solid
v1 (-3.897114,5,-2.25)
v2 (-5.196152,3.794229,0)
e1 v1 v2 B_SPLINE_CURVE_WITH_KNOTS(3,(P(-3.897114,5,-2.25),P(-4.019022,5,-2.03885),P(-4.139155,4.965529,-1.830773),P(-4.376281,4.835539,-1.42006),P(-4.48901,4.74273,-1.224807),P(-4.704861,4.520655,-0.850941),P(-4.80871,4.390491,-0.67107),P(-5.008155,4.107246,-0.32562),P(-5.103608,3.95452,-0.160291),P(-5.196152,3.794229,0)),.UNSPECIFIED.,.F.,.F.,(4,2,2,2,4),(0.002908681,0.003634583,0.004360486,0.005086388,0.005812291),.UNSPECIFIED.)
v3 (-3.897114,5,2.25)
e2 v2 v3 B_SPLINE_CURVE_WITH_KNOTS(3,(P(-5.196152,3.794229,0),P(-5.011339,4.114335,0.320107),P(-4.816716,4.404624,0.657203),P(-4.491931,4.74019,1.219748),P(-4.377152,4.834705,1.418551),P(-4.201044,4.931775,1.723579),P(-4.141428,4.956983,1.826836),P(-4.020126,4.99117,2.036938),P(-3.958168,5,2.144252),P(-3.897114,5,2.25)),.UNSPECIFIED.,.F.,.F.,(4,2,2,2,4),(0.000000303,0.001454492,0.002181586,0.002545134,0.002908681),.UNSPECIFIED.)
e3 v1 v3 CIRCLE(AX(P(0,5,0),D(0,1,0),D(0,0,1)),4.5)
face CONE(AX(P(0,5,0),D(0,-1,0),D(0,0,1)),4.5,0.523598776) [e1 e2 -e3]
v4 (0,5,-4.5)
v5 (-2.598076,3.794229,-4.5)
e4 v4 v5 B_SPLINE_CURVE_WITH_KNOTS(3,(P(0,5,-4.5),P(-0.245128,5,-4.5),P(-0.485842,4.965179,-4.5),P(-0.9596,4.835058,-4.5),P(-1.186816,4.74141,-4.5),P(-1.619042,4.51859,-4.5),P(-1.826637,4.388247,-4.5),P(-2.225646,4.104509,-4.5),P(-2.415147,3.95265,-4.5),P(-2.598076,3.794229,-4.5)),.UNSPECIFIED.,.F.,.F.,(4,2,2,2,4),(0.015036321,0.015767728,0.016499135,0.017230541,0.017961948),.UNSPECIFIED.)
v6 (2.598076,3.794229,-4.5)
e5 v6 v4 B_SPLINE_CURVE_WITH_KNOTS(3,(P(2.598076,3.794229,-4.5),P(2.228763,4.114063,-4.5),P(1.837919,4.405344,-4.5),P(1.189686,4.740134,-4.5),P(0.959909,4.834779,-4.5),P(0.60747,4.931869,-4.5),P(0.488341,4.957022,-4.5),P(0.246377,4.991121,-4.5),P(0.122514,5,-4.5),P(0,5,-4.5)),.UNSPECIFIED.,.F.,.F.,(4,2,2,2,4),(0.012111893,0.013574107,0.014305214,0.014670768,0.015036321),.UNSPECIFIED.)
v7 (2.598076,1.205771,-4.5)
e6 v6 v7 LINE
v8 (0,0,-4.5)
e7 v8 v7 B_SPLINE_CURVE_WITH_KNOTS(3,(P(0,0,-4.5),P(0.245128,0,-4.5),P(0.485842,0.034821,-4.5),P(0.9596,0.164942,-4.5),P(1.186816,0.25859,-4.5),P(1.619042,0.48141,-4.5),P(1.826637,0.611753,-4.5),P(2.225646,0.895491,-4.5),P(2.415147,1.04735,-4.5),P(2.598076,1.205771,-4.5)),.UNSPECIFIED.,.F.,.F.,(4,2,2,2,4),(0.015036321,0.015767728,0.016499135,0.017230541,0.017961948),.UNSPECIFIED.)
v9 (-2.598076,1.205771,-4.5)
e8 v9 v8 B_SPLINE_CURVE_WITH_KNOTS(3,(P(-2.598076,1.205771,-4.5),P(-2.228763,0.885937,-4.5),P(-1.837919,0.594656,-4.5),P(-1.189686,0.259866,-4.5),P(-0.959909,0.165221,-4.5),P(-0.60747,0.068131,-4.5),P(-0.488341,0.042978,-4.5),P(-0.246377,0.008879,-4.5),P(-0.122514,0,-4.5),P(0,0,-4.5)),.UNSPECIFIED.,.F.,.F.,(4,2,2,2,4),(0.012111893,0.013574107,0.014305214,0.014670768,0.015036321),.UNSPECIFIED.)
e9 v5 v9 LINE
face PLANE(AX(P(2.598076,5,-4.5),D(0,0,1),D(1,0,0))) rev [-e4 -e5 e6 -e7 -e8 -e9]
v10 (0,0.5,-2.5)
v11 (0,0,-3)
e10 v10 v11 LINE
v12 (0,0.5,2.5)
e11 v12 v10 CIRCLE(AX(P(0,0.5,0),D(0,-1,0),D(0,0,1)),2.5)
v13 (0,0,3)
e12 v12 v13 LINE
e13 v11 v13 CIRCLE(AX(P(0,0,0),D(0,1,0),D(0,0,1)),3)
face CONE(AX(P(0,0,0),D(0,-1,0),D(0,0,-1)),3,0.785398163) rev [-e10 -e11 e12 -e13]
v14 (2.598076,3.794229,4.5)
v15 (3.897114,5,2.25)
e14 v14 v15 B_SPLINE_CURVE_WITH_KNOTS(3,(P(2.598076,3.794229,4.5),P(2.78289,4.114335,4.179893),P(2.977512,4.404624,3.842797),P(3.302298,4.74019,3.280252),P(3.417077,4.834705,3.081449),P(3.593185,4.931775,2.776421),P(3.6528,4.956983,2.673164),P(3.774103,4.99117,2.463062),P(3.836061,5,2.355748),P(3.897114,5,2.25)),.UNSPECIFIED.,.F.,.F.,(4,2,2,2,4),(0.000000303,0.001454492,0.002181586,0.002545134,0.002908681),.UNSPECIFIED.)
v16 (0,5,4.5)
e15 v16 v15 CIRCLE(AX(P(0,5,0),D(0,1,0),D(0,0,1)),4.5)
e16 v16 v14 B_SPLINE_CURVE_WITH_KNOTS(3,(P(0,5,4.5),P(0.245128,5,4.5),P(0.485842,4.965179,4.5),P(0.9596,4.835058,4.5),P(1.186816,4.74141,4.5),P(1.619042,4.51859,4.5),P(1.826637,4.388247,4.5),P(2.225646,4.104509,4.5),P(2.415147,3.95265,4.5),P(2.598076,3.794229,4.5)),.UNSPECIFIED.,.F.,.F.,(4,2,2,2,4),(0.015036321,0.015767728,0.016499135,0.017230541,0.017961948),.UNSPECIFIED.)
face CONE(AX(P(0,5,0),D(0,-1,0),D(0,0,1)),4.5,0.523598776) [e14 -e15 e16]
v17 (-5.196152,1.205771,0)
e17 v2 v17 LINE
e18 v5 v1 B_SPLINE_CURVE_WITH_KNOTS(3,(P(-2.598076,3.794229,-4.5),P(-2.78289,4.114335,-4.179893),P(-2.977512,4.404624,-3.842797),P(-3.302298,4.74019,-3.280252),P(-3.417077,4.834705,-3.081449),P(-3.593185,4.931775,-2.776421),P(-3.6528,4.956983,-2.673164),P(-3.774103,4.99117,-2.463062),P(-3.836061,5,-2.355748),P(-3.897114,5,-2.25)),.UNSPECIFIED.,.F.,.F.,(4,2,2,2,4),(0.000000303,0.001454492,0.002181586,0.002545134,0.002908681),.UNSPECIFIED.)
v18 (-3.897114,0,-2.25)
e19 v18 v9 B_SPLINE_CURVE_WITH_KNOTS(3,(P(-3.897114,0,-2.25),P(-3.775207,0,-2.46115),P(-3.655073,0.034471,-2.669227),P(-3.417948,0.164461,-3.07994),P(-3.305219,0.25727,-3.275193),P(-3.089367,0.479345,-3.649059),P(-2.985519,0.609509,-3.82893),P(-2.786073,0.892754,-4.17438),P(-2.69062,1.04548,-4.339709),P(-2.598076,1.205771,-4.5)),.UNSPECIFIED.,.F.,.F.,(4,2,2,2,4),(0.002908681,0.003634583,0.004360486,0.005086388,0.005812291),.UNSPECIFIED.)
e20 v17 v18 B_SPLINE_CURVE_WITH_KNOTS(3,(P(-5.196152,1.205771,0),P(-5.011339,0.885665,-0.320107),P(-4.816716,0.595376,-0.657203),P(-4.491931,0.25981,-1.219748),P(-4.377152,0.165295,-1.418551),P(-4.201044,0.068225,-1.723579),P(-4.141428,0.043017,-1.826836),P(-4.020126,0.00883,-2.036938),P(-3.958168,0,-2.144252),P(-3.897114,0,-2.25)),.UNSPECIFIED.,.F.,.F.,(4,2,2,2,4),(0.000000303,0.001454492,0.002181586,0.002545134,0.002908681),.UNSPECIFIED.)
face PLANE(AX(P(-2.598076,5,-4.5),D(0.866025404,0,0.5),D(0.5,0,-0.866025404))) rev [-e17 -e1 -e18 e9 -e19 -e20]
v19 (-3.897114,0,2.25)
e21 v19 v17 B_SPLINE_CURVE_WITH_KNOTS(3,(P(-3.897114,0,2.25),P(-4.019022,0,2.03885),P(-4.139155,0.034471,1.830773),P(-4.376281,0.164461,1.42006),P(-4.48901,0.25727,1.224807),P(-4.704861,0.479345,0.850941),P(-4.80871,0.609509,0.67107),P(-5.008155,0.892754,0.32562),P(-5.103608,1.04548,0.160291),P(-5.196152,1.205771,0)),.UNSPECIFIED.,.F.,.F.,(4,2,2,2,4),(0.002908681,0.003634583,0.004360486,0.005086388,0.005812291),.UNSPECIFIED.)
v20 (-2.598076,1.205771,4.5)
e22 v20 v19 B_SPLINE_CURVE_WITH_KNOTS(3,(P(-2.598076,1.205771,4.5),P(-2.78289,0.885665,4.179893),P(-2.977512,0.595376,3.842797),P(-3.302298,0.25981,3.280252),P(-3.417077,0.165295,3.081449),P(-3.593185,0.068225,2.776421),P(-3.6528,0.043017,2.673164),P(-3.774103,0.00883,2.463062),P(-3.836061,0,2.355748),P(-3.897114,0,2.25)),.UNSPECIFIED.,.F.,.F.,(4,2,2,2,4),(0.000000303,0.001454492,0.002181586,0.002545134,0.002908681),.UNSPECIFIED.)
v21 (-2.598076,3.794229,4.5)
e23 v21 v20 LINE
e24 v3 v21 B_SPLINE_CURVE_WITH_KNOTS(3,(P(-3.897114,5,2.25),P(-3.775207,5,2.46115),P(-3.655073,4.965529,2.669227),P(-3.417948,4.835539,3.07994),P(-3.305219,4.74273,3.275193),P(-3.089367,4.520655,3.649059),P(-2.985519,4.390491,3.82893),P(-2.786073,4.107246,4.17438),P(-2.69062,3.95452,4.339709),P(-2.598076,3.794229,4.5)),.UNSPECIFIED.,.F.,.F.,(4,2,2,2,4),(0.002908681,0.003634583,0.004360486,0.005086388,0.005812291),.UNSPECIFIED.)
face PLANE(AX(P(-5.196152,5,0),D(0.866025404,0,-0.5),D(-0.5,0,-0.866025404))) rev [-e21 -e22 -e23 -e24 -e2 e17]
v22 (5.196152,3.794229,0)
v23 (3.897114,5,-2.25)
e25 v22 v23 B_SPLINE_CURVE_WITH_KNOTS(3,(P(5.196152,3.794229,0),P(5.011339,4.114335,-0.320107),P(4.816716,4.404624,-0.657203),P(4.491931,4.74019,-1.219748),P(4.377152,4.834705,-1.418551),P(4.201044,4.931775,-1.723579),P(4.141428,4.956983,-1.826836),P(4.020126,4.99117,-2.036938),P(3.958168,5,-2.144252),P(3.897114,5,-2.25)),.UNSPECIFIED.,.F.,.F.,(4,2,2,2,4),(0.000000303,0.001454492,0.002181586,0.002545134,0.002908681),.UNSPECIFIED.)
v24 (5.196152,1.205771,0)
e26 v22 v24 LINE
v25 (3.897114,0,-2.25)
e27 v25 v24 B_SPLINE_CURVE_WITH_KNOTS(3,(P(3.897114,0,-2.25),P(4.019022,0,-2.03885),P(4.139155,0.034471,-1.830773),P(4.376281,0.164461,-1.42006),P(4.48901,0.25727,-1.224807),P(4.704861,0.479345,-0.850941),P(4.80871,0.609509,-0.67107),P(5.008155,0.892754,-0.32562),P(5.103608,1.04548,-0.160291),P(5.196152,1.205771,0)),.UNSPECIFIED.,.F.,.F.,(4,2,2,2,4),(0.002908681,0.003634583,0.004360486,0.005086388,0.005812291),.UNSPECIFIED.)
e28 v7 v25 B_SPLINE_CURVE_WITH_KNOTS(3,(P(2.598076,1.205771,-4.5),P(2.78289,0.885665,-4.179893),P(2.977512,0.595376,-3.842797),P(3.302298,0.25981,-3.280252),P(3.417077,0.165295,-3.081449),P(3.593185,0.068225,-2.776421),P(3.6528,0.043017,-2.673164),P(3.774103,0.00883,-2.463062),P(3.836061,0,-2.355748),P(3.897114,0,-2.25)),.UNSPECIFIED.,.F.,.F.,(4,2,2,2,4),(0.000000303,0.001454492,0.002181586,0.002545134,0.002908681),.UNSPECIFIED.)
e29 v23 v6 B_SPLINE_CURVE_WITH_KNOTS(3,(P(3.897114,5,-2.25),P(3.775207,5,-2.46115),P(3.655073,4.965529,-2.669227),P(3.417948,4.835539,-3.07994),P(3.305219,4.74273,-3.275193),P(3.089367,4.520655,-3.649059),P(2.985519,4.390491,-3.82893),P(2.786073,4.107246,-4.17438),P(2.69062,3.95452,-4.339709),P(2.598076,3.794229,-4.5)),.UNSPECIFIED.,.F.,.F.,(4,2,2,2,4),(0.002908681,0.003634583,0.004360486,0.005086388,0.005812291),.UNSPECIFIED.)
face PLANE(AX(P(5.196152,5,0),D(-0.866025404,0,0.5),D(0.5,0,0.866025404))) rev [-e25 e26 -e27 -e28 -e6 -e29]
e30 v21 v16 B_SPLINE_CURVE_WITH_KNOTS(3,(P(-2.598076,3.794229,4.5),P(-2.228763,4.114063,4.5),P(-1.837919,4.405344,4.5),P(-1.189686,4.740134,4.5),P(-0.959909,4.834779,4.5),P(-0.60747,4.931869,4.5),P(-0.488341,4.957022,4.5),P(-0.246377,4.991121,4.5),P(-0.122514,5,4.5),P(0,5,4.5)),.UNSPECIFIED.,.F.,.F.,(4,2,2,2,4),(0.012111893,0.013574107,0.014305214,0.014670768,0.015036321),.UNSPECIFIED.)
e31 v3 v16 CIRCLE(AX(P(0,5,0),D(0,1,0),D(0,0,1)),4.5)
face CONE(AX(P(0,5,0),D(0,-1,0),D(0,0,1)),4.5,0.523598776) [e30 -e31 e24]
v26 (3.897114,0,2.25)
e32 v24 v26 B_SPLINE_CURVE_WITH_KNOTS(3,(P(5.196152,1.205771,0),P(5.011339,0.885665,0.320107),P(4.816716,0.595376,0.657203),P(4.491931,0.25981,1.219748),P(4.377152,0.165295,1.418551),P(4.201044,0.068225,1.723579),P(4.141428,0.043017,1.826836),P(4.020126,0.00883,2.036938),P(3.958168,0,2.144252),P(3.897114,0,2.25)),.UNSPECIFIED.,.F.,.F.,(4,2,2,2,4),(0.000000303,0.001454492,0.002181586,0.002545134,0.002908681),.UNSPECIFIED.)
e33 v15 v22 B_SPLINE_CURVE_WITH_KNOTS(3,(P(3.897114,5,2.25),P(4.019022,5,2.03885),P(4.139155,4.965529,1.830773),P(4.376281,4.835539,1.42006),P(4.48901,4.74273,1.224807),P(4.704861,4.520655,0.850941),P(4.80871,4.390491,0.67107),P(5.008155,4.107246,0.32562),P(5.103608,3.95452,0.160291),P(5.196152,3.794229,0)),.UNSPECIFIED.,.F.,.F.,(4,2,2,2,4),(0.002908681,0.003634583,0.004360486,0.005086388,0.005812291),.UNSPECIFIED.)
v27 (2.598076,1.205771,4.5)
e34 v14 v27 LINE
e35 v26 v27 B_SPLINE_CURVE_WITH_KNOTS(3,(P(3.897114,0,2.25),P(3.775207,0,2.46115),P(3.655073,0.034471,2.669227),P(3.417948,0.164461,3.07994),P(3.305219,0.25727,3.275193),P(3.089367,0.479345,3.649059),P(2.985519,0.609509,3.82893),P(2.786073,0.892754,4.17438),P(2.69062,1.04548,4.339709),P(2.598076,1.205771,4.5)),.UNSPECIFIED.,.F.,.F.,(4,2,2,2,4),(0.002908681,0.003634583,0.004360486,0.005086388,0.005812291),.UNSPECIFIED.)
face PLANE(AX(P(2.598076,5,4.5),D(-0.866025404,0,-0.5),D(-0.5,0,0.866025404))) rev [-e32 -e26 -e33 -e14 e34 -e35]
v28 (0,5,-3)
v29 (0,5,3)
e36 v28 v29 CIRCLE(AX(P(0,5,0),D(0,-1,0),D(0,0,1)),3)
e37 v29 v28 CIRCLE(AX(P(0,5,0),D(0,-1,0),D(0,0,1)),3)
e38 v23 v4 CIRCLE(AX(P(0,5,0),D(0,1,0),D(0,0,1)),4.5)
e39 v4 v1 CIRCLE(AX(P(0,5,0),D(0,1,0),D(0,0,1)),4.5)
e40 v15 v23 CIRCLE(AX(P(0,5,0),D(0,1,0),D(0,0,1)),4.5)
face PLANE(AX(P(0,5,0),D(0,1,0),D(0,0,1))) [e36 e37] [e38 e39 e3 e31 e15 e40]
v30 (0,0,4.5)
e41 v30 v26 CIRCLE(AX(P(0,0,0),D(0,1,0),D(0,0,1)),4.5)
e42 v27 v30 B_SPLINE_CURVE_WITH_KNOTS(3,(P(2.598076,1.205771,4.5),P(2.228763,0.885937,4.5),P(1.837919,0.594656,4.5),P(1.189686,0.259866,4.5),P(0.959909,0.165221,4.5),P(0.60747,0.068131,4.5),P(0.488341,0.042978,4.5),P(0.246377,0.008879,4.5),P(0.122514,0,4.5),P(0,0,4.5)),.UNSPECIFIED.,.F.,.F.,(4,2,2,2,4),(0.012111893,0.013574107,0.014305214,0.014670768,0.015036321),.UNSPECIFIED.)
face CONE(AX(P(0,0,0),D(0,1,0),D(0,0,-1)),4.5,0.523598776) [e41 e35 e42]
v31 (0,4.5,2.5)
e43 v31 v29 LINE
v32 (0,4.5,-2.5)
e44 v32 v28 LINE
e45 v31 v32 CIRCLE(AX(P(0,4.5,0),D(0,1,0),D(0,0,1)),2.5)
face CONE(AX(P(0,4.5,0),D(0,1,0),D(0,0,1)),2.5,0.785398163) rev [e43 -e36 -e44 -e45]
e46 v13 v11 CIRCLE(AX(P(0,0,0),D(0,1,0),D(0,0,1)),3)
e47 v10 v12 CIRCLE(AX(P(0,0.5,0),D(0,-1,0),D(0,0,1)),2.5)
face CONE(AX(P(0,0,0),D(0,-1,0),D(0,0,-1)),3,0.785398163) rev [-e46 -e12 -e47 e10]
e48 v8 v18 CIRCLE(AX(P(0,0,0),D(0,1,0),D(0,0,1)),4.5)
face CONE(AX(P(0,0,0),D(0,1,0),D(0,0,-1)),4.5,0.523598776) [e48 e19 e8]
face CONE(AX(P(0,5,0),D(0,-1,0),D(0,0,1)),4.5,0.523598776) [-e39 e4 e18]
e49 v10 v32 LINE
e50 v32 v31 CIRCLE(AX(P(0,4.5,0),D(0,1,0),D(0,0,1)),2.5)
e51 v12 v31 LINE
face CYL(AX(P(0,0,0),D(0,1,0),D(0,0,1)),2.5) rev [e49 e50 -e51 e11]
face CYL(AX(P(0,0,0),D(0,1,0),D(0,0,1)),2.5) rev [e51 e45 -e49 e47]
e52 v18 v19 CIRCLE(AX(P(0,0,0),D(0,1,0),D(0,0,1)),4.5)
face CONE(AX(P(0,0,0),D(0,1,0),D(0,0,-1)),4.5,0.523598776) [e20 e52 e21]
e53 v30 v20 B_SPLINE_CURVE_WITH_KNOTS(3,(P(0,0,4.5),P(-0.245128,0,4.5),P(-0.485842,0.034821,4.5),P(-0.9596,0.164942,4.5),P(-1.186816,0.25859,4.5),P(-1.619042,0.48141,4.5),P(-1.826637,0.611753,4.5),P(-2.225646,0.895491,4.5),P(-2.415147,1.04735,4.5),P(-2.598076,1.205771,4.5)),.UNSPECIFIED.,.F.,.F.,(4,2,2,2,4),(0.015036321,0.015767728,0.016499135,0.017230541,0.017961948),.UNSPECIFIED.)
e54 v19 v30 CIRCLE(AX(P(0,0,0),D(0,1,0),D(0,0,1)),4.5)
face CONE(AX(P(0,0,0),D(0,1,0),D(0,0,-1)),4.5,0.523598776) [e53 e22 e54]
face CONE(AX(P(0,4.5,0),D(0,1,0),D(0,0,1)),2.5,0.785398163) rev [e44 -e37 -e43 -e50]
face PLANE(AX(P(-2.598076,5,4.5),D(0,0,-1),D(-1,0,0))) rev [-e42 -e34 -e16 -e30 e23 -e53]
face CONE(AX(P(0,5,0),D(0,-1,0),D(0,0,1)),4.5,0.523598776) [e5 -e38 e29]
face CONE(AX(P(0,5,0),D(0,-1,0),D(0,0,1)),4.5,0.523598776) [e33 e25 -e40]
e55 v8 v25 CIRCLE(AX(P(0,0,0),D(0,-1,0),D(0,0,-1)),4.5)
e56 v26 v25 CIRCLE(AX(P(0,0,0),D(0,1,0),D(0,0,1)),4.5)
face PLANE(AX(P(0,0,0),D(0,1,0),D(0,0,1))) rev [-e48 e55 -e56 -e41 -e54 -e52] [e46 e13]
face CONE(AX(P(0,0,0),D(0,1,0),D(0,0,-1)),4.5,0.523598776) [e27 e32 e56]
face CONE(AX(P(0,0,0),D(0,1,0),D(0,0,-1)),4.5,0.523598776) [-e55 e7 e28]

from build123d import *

# Parameters (mm, degrees)
BOSS_EXTRUDE1_DEPTH = 5
SKETCH2_R           = 2.5
CUT_EXTRUDE1_DEPTH  = 5
SKETCH3_OUTSIDE_W   = 21.092
SKETCH3_OUTSIDE_H   = 19.7
SKETCH3_OUTSIDE_R   = 4.5
CUT_EXTRUDE2_DEPTH  = 5
CUT_EXTRUDE2_DRAFT  = -30
SKETCH4_OUTSIDE_W   = 21.092
SKETCH4_OUTSIDE_H   = 19.7
SKETCH4_OUTSIDE_R   = 4.5
CUT_EXTRUDE3_DEPTH  = 5
CUT_EXTRUDE3_DRAFT  = -30
CHAMFER1_SIZE       = 0.5
CHAMFER2_SIZE       = 0.5


with BuildPart() as part:
    # Sketch1 → Boss-Extrude1 (new body)
    with BuildSketch(Plane(origin=(0, 0, 0), x_dir=(1, 0, 0), z_dir=(0, 1, 0))):
        Polygon((2.598076211, 4.5), (-2.598076211, 4.5), (-5.196152423, 0), (-2.598076211, -4.5), (2.598076211, -4.5), (5.196152423, 0), align=None)
    extrude(amount=BOSS_EXTRUDE1_DEPTH)

    # Sketch2 → Cut-Extrude1 (cut)
    with BuildSketch(Plane(origin=(0, 5, 0), x_dir=(1, 0, 0), z_dir=(0, 1, 0))):
        with Locations(Location((0, 0, 0), (0, 0, 270))):
            Circle(SKETCH2_R)
    extrude(amount=-CUT_EXTRUDE1_DEPTH, mode=Mode.SUBTRACT)


with BuildPart() as cut_extrude2_tool:
    # Sketch3 outside → Cut-Extrude2 (with draft: the straight prism first)
    with BuildSketch(Plane(origin=(0, 5, 0), x_dir=(1, 0, 0), z_dir=(0, 1, 0))):
        Rectangle(SKETCH3_OUTSIDE_W, SKETCH3_OUTSIDE_H)
        Circle(SKETCH3_OUTSIDE_R, mode=Mode.SUBTRACT)
    extrude(amount=-CUT_EXTRUDE2_DEPTH)
    # Cut-Extrude2: the draft: its side faces are tilted about the plane it starts from
    cut_extrude2_sides = [cut_extrude2_tool.faces().sort_by_distance(p)[0] for p in [
        (0, 2.5, 9.85),
        (10.546, 2.5, 0),
        (0, 2.5, -9.85),
        (-10.546, 2.5, 0),
        (-4.5, 2.5, 0),
    ]]
    draft(cut_extrude2_sides, Plane(origin=(0, 5, 0), x_dir=(1, 0, 0), z_dir=(0, 1, 0)), CUT_EXTRUDE2_DRAFT)


with BuildPart() as part_1:
    add(part.part)

    # Cut-Extrude2: cut by cut_extrude2_tool
    add(cut_extrude2_tool.part, mode=Mode.SUBTRACT)


with BuildPart() as cut_extrude3_tool:
    # Sketch4 outside → Cut-Extrude3 (with draft: the straight prism first)
    with BuildSketch(Plane.XZ):
        Rectangle(SKETCH4_OUTSIDE_W, SKETCH4_OUTSIDE_H)
        Circle(SKETCH4_OUTSIDE_R, mode=Mode.SUBTRACT)
    extrude(amount=-CUT_EXTRUDE3_DEPTH)
    # Cut-Extrude3: the draft: its side faces are tilted about the plane it starts from
    cut_extrude3_sides = [cut_extrude3_tool.faces().sort_by_distance(p)[0] for p in [
        (0, 2.5, -9.85),
        (10.546, 2.5, 0),
        (0, 2.5, 9.85),
        (-10.546, 2.5, 0),
        (-4.5, 2.5, 0),
    ]]
    draft(cut_extrude3_sides, Plane.XZ, CUT_EXTRUDE3_DRAFT)


with BuildPart() as part_2:
    add(part_1.part)

    # Cut-Extrude3: cut by cut_extrude3_tool
    add(cut_extrude3_tool.part, mode=Mode.SUBTRACT)

    # Chamfer1
    chamfer1_edges = [part_2.edges().sort_by_distance(p)[0] for p in [
        (0, 5, -2.5),
    ]]
    chamfer(chamfer1_edges, length=CHAMFER1_SIZE)

    # Chamfer2
    chamfer2_edges = [part_2.edges().sort_by_distance(p)[0] for p in [
        (0, 0, -2.5),
    ]]
    chamfer(chamfer2_edges, length=CHAMFER2_SIZE)


solid = part_2.part
